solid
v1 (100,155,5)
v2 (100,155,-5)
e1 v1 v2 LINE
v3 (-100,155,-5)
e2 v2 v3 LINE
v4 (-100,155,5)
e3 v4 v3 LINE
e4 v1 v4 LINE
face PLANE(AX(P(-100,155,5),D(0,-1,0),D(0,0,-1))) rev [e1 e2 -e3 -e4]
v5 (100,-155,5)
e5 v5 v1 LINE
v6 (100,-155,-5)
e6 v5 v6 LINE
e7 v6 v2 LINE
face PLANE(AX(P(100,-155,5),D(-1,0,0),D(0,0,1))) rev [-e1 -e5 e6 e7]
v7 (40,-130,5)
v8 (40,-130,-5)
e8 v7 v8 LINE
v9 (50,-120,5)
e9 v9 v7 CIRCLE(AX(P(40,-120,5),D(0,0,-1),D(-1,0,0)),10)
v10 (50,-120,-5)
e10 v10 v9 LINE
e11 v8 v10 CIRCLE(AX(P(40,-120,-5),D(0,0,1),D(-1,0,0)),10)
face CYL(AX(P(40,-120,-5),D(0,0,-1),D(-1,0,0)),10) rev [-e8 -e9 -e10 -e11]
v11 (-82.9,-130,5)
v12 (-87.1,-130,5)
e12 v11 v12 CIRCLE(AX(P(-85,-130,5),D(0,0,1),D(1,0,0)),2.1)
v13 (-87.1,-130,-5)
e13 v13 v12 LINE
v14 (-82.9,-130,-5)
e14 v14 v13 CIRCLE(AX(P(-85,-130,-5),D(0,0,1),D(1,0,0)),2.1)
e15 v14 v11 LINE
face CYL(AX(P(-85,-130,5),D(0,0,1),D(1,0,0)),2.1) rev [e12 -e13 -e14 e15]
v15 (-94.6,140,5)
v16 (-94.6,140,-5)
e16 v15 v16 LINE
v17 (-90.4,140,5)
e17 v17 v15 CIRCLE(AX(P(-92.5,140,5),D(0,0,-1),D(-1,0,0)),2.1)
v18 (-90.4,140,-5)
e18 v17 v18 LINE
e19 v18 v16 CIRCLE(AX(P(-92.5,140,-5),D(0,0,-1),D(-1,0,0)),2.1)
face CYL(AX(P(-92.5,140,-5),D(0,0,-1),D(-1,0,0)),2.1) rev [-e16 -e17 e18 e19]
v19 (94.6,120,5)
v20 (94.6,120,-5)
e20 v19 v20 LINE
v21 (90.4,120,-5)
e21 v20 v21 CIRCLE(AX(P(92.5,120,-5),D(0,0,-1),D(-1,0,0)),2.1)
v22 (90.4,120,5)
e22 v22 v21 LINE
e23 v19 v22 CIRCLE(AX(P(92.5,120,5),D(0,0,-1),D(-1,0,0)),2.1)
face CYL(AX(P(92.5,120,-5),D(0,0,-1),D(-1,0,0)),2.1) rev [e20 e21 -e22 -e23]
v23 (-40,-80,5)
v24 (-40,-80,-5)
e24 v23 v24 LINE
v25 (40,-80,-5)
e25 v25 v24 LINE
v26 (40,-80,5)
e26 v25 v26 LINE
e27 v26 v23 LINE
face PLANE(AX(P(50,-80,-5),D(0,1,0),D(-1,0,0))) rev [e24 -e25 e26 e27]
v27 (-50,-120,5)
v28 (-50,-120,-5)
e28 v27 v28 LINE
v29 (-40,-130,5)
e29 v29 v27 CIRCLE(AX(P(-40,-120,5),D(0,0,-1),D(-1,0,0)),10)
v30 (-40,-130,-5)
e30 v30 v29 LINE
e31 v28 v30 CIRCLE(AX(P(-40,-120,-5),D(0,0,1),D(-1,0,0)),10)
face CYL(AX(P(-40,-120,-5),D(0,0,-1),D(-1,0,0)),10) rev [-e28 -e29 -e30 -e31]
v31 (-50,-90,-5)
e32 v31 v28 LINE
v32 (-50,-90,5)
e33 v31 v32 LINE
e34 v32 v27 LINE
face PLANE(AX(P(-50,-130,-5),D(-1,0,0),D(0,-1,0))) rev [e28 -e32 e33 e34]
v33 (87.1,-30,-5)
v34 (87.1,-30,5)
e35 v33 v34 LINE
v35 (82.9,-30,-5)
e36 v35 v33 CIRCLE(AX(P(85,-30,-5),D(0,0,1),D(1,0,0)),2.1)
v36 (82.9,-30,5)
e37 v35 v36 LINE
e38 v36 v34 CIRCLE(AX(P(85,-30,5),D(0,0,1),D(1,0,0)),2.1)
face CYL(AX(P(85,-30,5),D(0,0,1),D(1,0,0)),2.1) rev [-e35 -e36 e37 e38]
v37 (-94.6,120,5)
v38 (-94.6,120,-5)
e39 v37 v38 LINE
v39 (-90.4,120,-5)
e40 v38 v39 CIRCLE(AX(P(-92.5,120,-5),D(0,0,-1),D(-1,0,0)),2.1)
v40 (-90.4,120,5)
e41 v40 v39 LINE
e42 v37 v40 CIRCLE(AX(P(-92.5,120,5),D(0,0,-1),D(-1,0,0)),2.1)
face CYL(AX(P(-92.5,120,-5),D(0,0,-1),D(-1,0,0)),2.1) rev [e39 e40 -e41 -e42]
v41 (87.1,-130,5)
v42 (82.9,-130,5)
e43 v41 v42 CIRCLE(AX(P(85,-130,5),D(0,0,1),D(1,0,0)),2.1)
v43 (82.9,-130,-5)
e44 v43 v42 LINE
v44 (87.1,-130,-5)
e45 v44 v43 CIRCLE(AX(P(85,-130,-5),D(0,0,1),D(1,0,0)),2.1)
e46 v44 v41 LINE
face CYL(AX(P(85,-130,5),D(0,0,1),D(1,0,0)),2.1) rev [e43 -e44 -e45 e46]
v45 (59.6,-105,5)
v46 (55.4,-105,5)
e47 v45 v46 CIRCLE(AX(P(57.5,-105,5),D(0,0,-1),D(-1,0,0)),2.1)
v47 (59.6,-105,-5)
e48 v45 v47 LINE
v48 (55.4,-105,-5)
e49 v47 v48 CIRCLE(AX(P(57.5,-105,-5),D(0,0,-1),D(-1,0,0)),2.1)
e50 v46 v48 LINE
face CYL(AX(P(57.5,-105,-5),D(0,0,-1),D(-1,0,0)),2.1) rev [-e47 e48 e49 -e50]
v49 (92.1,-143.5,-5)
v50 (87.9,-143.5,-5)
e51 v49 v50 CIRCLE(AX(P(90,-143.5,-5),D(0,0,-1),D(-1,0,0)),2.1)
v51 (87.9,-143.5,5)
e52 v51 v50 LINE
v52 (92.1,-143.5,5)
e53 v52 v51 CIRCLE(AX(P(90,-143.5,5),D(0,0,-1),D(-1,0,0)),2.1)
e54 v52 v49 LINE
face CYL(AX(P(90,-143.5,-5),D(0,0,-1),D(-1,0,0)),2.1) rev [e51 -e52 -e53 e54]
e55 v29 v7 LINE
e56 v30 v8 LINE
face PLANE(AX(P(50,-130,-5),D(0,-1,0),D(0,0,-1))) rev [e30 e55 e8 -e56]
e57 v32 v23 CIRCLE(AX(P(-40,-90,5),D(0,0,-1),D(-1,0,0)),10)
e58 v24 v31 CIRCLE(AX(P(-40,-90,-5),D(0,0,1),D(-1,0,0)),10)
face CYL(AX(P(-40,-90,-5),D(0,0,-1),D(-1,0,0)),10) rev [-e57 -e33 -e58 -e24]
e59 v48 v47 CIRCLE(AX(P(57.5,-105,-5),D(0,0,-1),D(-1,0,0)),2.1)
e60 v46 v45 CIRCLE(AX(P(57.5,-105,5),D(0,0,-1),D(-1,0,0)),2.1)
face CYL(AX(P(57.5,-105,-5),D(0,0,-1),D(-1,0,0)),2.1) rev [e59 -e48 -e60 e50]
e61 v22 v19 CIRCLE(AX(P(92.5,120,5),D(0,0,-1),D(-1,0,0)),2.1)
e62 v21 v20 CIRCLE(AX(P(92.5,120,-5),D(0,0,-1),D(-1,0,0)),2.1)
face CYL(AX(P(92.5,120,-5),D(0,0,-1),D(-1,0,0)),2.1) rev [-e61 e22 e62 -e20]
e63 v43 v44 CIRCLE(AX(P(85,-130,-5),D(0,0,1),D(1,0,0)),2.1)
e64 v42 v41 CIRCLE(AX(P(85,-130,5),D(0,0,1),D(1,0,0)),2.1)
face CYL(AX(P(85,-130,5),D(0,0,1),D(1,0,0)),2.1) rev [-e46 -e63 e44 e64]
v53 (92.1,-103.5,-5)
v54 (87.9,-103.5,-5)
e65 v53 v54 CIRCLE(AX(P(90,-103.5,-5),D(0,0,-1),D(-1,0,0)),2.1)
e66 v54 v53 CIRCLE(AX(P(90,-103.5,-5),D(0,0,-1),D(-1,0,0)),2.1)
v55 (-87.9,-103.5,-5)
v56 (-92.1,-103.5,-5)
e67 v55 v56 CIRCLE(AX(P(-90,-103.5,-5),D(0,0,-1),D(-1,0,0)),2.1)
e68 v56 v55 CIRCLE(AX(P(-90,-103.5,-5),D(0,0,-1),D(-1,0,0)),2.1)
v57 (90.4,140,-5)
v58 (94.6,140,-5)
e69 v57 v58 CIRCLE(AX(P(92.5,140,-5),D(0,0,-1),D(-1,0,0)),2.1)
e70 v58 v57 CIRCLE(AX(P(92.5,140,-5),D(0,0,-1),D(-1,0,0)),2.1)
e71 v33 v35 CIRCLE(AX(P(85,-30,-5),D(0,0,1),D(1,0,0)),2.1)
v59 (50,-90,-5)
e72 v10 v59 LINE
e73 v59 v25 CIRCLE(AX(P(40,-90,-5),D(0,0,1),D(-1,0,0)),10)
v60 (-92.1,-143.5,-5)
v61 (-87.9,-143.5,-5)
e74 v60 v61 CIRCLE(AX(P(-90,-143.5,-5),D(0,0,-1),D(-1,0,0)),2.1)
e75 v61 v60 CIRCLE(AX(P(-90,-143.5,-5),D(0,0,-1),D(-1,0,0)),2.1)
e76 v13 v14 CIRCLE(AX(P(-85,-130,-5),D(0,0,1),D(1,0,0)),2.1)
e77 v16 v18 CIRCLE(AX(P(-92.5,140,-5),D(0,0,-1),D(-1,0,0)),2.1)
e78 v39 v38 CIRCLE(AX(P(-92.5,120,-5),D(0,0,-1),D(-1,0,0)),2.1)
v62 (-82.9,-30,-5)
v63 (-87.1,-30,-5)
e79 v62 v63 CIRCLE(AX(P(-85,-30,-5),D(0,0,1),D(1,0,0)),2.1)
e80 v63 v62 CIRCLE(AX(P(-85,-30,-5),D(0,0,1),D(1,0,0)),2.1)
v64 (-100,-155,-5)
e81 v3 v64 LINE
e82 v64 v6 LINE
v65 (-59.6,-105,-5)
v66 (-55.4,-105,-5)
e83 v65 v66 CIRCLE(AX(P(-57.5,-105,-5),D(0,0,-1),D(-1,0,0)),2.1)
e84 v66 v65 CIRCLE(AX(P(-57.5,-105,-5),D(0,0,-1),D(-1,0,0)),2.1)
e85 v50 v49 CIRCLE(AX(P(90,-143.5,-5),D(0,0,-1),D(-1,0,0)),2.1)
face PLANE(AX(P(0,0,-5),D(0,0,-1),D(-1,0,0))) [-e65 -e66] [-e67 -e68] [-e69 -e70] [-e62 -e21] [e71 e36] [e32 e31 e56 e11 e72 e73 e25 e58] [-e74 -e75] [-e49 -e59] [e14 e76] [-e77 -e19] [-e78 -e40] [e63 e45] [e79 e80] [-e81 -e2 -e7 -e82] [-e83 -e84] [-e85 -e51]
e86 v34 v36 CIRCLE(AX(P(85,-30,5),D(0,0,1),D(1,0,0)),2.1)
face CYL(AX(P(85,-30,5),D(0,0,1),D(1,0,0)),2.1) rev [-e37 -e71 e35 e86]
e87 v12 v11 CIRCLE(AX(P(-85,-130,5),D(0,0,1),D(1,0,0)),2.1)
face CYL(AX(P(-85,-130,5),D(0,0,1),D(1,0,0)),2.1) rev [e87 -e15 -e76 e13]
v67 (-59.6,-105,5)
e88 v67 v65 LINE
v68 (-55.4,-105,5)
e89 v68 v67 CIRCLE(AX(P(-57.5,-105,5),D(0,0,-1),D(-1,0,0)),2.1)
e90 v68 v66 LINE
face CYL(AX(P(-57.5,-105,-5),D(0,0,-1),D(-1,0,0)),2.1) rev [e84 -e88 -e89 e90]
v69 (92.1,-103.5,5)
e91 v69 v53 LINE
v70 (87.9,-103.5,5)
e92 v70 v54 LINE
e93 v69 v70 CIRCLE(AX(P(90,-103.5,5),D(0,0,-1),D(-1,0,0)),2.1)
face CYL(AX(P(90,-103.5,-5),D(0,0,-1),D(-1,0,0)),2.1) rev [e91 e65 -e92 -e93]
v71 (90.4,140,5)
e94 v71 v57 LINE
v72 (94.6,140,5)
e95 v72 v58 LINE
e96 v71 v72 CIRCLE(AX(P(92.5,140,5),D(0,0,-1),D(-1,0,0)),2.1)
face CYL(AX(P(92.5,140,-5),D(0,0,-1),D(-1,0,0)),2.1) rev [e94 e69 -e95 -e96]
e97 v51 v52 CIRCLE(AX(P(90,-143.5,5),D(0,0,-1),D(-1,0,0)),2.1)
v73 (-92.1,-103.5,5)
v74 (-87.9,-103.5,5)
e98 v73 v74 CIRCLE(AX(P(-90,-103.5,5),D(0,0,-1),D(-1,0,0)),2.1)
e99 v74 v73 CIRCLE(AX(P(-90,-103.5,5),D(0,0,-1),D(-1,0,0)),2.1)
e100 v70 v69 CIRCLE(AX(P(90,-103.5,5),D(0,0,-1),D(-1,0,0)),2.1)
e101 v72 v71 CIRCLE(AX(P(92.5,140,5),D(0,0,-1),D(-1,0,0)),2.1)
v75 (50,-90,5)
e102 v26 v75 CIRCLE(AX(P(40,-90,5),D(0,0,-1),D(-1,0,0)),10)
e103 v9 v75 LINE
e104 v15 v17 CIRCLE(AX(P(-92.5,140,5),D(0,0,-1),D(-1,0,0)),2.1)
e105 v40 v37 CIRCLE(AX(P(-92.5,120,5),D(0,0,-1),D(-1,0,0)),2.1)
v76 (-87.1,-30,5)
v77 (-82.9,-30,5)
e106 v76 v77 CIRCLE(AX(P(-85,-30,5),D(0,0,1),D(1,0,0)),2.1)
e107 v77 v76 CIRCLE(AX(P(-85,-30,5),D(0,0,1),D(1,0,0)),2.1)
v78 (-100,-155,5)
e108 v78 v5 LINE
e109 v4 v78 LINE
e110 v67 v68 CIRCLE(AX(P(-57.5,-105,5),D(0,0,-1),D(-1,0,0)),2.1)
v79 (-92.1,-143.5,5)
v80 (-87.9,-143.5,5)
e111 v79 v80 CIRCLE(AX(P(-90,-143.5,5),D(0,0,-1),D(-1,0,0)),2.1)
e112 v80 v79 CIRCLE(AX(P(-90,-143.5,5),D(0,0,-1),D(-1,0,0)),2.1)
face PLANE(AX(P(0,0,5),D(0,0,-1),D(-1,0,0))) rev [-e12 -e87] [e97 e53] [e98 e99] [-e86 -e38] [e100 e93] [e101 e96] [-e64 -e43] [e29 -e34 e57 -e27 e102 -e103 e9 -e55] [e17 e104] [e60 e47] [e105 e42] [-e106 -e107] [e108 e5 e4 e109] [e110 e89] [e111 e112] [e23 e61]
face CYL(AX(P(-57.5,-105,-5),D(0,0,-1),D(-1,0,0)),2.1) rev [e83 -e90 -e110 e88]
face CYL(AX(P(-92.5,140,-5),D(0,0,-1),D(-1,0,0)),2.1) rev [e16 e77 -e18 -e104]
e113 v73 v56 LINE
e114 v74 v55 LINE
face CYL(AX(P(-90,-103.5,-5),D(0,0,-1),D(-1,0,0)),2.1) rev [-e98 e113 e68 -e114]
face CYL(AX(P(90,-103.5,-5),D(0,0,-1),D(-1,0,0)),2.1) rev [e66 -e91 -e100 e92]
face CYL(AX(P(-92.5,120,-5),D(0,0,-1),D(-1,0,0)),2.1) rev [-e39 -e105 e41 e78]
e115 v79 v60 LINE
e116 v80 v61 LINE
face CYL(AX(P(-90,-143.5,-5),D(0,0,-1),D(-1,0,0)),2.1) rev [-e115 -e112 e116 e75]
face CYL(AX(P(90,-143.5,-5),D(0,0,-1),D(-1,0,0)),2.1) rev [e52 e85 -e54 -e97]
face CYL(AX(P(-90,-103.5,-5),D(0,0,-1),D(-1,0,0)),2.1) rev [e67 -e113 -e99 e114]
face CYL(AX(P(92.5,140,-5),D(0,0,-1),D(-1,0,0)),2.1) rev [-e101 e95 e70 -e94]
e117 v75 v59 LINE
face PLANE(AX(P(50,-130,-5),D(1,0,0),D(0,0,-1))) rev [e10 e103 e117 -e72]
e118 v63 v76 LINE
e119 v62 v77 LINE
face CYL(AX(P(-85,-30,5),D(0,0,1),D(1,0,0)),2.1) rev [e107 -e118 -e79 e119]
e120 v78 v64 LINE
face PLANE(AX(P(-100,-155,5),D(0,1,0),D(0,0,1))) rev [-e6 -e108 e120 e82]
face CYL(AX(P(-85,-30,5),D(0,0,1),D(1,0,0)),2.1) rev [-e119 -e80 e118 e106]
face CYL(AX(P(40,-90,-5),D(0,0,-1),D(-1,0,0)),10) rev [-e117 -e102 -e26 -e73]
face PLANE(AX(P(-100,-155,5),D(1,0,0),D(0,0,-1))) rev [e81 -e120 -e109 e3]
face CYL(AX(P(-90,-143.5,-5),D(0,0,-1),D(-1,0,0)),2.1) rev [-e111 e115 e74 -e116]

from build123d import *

# Parameters (mm, degrees)
SKETCH_1_W          = 200
SKETCH_1_H          = 310
EXTRUDE_1_DEPTH     = 5
SKETCH_2_W          = 100
SKETCH_2_H          = 50
CUT_EXTRUDE_1_DEPTH = 185.729532019
HOLE_WIZARD_M5_2_D  = 4.2
FILLET_1_R          = 10
HOLE_WIZARD_M5_4_D  = 4.2
HOLE_WIZARD_M5_5_D  = 4.2
HOLE_WIZARD_M5_6_D  = 4.2


with BuildPart() as part:
    # 草图1 → 凸台-拉伸1 (new, symmetric)
    with BuildSketch(Plane.XY):
        Rectangle(SKETCH_1_W, SKETCH_1_H)
    extrude(amount=EXTRUDE_1_DEPTH, both=True)

    # 草图2 → 切除-拉伸1 (cut, through all)
    with BuildSketch(Plane.XY.offset(5)):
        with Locations((0, -105)):
            Rectangle(SKETCH_2_W, SKETCH_2_H)
    extrude(amount=-CUT_EXTRUDE_1_DEPTH, mode=Mode.SUBTRACT)

    # M5 螺纹孔2 (through all)
    with Locations(Plane.XY.offset(5)):
        with Locations((85, -130), (85, -30), (-85, -30), (-85, -130)):
            Hole(HOLE_WIZARD_M5_2_D / 2)

    # 圆角1
    fillet_1_edges = [part.edges().sort_by_distance(p)[0] for p in [
        (50, -80, 0),
        (50, -130, 0),
        (-50, -130, 0),
        (-50, -80, 0),
    ]]
    fillet(fillet_1_edges, radius=FILLET_1_R)

    # M5 螺纹孔4 (through all)
    with Locations(Plane(origin=(0, 0, -5), x_dir=(-1, 0, 0), z_dir=(0, 0, -1))):
        with Locations((92.5, 120), (92.5, 140), (-92.5, 140), (-92.5, 120)):
            Hole(HOLE_WIZARD_M5_4_D / 2)

    # M5 螺纹孔5 (through all)
    with Locations(Plane(origin=(0, 0, -5), x_dir=(-1, 0, 0), z_dir=(0, 0, -1))):
        with Locations((-57.5, -105), (57.5, -105)):
            Hole(HOLE_WIZARD_M5_5_D / 2)

    # M5 螺纹孔6 (through all)
    with Locations(Plane(origin=(0, 0, -5), x_dir=(-1, 0, 0), z_dir=(0, 0, -1))):
        with Locations((90, -143.5), (90, -103.5), (-90, -103.5), (-90, -143.5)):
            Hole(HOLE_WIZARD_M5_6_D / 2)


solid = part.part
